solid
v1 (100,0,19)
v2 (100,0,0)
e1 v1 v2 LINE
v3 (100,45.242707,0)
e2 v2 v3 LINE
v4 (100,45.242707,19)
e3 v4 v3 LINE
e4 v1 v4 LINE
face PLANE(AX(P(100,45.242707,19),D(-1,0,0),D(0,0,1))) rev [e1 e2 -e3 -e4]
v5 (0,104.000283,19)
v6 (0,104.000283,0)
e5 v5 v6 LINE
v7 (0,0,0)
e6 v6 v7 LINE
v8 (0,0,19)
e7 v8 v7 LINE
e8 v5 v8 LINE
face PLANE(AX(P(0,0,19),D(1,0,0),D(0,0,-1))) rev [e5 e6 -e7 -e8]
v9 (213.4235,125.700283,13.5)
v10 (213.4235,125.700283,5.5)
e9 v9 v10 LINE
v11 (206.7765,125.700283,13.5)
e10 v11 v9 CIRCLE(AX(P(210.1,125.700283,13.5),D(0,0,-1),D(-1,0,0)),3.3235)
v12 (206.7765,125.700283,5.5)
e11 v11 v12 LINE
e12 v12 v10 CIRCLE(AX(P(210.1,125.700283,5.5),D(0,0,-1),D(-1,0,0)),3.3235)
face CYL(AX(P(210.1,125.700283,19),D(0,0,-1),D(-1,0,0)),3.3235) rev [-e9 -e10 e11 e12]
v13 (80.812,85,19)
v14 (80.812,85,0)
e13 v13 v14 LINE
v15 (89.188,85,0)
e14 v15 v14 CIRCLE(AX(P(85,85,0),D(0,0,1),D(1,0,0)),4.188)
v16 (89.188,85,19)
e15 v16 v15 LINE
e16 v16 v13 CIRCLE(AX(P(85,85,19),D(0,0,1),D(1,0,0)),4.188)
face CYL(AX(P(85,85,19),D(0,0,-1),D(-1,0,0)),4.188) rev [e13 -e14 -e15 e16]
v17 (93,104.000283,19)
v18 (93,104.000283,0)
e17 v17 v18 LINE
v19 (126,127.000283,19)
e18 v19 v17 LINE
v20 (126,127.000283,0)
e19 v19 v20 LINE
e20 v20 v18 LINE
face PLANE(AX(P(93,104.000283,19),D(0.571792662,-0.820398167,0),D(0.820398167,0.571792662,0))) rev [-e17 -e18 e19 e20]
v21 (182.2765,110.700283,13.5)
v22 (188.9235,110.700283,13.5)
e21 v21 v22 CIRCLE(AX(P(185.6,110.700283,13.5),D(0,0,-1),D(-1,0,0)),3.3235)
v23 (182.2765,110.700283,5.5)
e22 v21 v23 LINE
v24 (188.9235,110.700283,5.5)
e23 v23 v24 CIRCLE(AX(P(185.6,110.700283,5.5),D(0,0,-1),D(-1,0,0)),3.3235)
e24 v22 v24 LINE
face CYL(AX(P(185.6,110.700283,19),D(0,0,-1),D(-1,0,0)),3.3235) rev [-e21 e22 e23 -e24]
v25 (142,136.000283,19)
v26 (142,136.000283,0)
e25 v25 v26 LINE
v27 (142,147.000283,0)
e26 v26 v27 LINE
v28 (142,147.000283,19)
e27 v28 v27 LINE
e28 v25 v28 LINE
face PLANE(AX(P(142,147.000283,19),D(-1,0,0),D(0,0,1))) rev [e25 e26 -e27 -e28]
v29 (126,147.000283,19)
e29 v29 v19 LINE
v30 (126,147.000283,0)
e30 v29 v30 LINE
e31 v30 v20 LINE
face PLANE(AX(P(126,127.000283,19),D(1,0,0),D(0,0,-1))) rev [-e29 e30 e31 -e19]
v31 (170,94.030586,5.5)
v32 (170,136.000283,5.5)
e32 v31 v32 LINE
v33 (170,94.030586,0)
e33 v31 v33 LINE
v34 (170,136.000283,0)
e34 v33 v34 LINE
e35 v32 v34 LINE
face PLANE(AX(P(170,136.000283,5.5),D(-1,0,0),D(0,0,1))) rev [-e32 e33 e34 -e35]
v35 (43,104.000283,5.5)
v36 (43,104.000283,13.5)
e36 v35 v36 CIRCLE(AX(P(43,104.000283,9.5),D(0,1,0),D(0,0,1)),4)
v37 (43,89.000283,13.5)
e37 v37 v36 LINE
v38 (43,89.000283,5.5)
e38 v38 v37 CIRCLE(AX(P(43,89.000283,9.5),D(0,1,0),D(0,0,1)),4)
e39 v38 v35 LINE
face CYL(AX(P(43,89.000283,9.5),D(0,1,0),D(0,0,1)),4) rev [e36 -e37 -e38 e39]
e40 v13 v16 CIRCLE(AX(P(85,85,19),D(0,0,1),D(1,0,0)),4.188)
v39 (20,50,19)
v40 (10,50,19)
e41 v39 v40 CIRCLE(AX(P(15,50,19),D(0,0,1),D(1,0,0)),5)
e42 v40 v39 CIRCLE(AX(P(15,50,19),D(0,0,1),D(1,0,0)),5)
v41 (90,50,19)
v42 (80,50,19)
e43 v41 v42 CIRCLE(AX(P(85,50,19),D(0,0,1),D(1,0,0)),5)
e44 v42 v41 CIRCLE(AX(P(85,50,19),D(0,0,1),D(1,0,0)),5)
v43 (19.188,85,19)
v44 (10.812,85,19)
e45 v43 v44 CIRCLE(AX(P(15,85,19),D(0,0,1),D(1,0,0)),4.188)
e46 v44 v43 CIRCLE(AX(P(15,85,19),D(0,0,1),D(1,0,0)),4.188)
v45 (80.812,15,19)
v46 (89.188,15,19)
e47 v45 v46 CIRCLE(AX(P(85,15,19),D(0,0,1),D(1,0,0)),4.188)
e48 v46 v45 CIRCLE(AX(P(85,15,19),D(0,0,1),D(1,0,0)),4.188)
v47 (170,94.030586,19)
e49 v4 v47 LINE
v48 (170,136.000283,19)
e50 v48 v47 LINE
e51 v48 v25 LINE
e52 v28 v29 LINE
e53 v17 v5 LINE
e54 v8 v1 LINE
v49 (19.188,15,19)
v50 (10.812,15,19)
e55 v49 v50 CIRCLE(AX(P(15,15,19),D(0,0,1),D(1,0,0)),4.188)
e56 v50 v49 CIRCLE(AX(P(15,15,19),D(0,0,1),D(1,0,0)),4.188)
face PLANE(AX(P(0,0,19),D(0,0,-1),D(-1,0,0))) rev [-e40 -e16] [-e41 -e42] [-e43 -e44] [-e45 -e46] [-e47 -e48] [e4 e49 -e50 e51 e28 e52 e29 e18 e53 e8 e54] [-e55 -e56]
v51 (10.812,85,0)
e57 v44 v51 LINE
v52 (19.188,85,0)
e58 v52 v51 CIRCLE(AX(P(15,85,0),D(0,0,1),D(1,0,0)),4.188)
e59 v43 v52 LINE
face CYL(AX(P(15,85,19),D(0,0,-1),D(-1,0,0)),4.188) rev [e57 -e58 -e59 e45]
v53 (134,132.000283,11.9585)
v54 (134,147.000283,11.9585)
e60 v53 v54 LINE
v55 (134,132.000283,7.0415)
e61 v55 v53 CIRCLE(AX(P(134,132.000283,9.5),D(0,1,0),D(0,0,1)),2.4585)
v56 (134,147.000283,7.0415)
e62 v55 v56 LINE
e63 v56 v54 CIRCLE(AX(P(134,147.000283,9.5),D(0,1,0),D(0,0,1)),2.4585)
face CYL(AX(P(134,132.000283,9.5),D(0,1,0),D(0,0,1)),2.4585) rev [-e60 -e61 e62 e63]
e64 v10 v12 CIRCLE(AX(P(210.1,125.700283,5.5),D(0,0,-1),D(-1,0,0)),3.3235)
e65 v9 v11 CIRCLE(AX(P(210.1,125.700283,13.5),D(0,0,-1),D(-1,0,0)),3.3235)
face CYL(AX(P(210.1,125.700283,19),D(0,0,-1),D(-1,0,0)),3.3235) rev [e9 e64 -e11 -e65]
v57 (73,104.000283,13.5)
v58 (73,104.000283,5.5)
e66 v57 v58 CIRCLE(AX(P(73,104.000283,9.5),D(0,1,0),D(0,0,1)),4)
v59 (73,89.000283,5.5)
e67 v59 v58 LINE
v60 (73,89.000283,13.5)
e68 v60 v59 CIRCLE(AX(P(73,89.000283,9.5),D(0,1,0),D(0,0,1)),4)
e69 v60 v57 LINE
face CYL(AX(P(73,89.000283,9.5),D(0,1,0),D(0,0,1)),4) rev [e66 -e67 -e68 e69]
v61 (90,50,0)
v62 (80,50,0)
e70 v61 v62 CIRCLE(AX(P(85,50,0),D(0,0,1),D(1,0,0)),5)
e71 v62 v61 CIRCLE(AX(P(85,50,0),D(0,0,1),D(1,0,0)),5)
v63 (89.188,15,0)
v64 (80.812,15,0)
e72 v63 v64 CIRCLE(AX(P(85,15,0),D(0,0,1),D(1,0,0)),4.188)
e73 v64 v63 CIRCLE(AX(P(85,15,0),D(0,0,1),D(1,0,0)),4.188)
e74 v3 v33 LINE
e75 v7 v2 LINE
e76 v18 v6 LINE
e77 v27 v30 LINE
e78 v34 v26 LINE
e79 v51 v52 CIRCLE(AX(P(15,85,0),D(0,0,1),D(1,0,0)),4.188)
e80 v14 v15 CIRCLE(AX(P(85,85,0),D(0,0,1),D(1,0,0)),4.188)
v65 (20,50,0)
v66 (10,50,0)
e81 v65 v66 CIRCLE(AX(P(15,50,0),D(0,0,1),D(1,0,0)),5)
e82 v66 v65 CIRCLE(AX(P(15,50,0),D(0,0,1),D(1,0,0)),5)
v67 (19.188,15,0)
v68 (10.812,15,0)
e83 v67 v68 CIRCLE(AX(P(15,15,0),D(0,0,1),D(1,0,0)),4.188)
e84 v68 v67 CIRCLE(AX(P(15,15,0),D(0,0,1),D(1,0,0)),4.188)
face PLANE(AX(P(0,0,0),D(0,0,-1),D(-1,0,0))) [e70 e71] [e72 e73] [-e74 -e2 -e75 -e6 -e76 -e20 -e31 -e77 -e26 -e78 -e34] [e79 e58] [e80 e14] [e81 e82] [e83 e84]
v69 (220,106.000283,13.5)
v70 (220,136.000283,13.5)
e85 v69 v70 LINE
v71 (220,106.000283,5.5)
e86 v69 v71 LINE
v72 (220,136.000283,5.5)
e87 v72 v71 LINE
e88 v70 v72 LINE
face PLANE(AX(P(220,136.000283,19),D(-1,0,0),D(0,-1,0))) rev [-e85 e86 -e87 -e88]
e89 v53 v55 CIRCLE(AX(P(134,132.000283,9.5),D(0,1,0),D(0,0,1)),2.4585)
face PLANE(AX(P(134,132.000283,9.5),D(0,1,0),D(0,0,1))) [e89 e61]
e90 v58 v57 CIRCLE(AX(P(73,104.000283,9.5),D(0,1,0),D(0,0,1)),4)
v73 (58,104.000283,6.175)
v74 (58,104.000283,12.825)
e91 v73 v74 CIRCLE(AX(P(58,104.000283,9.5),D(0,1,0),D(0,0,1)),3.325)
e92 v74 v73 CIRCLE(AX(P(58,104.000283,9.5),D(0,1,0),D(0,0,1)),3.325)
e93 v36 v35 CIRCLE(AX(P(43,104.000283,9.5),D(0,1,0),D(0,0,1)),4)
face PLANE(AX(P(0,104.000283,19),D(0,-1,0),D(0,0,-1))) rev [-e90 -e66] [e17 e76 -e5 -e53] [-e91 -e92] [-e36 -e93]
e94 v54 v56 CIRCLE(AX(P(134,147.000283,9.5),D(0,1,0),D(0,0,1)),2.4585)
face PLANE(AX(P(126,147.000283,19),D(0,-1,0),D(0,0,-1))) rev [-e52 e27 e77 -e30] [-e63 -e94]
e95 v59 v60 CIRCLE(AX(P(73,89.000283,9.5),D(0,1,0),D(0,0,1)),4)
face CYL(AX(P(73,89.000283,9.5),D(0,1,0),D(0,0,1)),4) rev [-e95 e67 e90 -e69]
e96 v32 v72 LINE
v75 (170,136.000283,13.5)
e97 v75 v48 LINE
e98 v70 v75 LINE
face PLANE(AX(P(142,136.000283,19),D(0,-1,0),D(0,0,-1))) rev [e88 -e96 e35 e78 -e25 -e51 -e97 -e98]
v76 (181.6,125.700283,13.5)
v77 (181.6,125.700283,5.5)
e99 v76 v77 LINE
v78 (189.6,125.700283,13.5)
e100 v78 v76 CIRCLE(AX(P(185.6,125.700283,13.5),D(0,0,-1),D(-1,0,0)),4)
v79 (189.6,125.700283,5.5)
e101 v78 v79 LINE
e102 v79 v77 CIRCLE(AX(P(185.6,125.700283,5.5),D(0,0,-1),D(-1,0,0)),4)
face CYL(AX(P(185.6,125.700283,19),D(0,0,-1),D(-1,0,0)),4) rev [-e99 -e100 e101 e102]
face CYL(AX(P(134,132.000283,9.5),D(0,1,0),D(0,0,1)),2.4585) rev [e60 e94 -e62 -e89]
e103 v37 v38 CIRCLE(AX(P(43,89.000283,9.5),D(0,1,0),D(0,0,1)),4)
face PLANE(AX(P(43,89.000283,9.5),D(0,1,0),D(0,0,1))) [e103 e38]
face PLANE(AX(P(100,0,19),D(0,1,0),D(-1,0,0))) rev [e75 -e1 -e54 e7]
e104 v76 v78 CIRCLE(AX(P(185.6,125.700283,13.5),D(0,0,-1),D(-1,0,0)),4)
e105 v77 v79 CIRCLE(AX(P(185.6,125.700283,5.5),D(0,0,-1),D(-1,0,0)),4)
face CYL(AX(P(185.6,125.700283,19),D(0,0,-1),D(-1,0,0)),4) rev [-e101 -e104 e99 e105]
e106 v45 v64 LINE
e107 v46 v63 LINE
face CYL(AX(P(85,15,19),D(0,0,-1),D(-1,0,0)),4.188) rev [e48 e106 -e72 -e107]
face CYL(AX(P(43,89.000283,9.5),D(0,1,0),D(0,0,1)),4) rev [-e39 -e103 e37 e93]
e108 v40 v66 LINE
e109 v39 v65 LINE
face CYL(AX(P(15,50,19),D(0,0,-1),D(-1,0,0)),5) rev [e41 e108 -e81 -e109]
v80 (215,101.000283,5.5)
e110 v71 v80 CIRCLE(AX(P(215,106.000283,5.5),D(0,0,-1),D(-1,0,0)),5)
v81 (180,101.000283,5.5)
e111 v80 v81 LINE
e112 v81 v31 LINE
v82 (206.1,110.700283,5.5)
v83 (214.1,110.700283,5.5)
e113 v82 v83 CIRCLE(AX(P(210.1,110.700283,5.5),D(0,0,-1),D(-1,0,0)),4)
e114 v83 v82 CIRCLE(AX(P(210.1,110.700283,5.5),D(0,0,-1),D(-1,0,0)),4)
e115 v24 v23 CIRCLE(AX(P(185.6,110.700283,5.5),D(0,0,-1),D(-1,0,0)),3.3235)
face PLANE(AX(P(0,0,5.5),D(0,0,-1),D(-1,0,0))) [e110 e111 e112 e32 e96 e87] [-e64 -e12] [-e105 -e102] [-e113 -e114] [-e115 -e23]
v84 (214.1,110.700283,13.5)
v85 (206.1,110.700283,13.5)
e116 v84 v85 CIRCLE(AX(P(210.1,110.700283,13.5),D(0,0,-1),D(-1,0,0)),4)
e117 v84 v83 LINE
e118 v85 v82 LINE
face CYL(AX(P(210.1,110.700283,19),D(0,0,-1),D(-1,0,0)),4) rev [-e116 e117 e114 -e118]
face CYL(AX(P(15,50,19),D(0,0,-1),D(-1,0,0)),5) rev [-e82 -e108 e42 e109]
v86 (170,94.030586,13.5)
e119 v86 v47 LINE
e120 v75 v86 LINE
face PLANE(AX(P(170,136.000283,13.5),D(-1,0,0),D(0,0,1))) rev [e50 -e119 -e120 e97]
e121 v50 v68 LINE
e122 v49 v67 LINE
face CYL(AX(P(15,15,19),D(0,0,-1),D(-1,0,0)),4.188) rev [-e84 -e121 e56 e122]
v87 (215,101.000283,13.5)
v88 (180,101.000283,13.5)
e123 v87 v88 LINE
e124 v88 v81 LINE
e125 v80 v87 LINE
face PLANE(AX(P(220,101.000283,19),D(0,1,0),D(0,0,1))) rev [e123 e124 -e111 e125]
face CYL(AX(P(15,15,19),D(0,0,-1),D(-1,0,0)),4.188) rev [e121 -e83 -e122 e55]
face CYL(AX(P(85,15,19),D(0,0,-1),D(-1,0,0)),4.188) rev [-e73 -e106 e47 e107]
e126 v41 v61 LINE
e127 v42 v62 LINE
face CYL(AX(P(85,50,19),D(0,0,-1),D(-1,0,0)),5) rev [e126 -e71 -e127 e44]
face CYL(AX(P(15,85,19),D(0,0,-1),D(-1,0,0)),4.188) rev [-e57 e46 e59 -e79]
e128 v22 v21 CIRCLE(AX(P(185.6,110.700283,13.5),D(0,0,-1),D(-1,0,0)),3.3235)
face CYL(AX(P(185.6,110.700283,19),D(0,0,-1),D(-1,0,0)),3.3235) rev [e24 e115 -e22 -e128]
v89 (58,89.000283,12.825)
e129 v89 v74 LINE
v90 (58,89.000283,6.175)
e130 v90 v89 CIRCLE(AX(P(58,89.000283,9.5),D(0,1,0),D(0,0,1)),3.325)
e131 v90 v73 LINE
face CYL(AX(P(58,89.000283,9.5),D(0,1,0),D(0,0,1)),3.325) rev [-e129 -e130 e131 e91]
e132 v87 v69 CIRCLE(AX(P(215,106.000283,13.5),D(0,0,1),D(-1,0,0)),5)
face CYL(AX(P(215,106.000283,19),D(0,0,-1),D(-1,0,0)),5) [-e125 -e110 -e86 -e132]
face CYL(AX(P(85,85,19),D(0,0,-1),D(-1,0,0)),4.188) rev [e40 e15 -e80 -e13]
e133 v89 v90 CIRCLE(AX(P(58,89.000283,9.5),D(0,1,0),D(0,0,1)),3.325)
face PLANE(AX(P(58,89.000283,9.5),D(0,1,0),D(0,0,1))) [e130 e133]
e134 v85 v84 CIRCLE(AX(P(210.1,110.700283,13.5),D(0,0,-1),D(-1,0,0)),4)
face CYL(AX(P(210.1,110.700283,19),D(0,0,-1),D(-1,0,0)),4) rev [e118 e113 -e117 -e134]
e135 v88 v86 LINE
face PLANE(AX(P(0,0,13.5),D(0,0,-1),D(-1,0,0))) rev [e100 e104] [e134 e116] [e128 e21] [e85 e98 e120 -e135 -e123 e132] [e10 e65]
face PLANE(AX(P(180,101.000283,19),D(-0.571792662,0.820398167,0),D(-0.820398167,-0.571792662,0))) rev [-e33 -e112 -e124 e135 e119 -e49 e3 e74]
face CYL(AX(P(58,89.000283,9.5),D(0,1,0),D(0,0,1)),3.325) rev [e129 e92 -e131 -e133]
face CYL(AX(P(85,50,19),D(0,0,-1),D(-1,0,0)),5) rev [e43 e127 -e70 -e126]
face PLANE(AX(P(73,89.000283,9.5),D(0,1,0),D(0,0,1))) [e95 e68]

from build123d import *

# Parameters (mm, degrees)
SKETCH1_R           = 4.188
SKETCH1_R_2         = 5
SKETCH1_R_3         = 3.3235
SKETCH1_R_4         = 4
BOSS_EXTRUDE1_DEPTH = 19
SKETCH2_R           = 4
SKETCH2_R_2         = 3.325
CUT_EXTRUDE1_DEPTH  = 15
SKETCH3_R           = 2.4585
CUT_EXTRUDE2_DEPTH  = 15
SKETCH4_W           = 50
SKETCH4_H           = 41.969696972
CUT_EXTRUDE3_DEPTH  = 5.5
SKETCH5_W           = 50
SKETCH5_H           = 41.969696972
CUT_EXTRUDE4_DEPTH  = 5.5
FILLET1_R           = 5


with BuildPart() as part:
    # Sketch1 → Boss-Extrude1 (new body)
    with BuildSketch(Plane.XY):
        Polygon((0, 0), (0, 104.0002829), (93, 104.0002829), (126, 127.0002829), (126, 147.0002829), (142, 147.0002829), (142, 136.0002829), (220, 136.0002829), (220, 101.000282896), (179.999999997, 101.000282896), (100, 45.24270714), (100, 0), align=None)
        with Locations((15, 15)):
            Circle(SKETCH1_R, mode=Mode.SUBTRACT)
        with Locations((15, 50)):
            Circle(SKETCH1_R_2, mode=Mode.SUBTRACT)
        with Locations((15, 85)):
            Circle(SKETCH1_R, mode=Mode.SUBTRACT)
        with Locations((85, 85)):
            Circle(SKETCH1_R, mode=Mode.SUBTRACT)
        with Locations((85, 50)):
            Circle(SKETCH1_R_2, mode=Mode.SUBTRACT)
        with Locations((85, 15)):
            Circle(SKETCH1_R, mode=Mode.SUBTRACT)
        with Locations((210.1, 125.7002829)):
            Circle(SKETCH1_R_3, mode=Mode.SUBTRACT)
        with Locations((210.1, 110.7002829)):
            Circle(SKETCH1_R_4, mode=Mode.SUBTRACT)
        with Locations((185.6, 110.7002829)):
            Circle(SKETCH1_R_3, mode=Mode.SUBTRACT)
        with Locations((185.6, 125.7002829)):
            Circle(SKETCH1_R_4, mode=Mode.SUBTRACT)
    extrude(amount=BOSS_EXTRUDE1_DEPTH)

    # Sketch2 → Cut-Extrude1 (cut)
    with BuildSketch(Plane(origin=(0, 104.0002829, 0), x_dir=(1, 0, 0), z_dir=(0, 1, 0))):
        with Locations(Location((43, -9.5, 0), (0, 0, 270))):
            Circle(SKETCH2_R)
        with Locations(Location((58, -9.5, 0), (0, 0, 270))):
            Circle(SKETCH2_R_2)
        with Locations(Location((73, -9.5, 0), (0, 0, 270))):
            Circle(SKETCH2_R)
    extrude(amount=-CUT_EXTRUDE1_DEPTH, mode=Mode.SUBTRACT)

    # Sketch3 → Cut-Extrude2 (cut)
    with BuildSketch(Plane(origin=(0, 147.0002829, 0), x_dir=(1, 0, 0), z_dir=(0, 1, 0))):
        with Locations(Location((134, -9.5, 0), (0, 0, 270))):
            Circle(SKETCH3_R)
    extrude(amount=-CUT_EXTRUDE2_DEPTH, mode=Mode.SUBTRACT)

    # Sketch4 → Cut-Extrude3 (cut)
    with BuildSketch(Plane.XY.offset(19)):
        with Locations((195, 115.015434414)):
            Rectangle(SKETCH4_W, SKETCH4_H)
    extrude(amount=-CUT_EXTRUDE3_DEPTH, mode=Mode.SUBTRACT)

    # Sketch5 → Cut-Extrude4 (cut)
    with BuildSketch(Plane(origin=(0, 0, 0), x_dir=(-1, 0, 0), z_dir=(0, 0, -1))):
        with Locations((-195, 115.015434414)):
            Rectangle(SKETCH5_W, SKETCH5_H)
    extrude(amount=-CUT_EXTRUDE4_DEPTH, mode=Mode.SUBTRACT)

    # Fillet1
    fillet1_edges = [part.edges().sort_by_distance(p)[0] for p in [
        (220, 101.000282896, 9.5),
    ]]
    fillet(fillet1_edges, radius=FILLET1_R)


solid = part.part
